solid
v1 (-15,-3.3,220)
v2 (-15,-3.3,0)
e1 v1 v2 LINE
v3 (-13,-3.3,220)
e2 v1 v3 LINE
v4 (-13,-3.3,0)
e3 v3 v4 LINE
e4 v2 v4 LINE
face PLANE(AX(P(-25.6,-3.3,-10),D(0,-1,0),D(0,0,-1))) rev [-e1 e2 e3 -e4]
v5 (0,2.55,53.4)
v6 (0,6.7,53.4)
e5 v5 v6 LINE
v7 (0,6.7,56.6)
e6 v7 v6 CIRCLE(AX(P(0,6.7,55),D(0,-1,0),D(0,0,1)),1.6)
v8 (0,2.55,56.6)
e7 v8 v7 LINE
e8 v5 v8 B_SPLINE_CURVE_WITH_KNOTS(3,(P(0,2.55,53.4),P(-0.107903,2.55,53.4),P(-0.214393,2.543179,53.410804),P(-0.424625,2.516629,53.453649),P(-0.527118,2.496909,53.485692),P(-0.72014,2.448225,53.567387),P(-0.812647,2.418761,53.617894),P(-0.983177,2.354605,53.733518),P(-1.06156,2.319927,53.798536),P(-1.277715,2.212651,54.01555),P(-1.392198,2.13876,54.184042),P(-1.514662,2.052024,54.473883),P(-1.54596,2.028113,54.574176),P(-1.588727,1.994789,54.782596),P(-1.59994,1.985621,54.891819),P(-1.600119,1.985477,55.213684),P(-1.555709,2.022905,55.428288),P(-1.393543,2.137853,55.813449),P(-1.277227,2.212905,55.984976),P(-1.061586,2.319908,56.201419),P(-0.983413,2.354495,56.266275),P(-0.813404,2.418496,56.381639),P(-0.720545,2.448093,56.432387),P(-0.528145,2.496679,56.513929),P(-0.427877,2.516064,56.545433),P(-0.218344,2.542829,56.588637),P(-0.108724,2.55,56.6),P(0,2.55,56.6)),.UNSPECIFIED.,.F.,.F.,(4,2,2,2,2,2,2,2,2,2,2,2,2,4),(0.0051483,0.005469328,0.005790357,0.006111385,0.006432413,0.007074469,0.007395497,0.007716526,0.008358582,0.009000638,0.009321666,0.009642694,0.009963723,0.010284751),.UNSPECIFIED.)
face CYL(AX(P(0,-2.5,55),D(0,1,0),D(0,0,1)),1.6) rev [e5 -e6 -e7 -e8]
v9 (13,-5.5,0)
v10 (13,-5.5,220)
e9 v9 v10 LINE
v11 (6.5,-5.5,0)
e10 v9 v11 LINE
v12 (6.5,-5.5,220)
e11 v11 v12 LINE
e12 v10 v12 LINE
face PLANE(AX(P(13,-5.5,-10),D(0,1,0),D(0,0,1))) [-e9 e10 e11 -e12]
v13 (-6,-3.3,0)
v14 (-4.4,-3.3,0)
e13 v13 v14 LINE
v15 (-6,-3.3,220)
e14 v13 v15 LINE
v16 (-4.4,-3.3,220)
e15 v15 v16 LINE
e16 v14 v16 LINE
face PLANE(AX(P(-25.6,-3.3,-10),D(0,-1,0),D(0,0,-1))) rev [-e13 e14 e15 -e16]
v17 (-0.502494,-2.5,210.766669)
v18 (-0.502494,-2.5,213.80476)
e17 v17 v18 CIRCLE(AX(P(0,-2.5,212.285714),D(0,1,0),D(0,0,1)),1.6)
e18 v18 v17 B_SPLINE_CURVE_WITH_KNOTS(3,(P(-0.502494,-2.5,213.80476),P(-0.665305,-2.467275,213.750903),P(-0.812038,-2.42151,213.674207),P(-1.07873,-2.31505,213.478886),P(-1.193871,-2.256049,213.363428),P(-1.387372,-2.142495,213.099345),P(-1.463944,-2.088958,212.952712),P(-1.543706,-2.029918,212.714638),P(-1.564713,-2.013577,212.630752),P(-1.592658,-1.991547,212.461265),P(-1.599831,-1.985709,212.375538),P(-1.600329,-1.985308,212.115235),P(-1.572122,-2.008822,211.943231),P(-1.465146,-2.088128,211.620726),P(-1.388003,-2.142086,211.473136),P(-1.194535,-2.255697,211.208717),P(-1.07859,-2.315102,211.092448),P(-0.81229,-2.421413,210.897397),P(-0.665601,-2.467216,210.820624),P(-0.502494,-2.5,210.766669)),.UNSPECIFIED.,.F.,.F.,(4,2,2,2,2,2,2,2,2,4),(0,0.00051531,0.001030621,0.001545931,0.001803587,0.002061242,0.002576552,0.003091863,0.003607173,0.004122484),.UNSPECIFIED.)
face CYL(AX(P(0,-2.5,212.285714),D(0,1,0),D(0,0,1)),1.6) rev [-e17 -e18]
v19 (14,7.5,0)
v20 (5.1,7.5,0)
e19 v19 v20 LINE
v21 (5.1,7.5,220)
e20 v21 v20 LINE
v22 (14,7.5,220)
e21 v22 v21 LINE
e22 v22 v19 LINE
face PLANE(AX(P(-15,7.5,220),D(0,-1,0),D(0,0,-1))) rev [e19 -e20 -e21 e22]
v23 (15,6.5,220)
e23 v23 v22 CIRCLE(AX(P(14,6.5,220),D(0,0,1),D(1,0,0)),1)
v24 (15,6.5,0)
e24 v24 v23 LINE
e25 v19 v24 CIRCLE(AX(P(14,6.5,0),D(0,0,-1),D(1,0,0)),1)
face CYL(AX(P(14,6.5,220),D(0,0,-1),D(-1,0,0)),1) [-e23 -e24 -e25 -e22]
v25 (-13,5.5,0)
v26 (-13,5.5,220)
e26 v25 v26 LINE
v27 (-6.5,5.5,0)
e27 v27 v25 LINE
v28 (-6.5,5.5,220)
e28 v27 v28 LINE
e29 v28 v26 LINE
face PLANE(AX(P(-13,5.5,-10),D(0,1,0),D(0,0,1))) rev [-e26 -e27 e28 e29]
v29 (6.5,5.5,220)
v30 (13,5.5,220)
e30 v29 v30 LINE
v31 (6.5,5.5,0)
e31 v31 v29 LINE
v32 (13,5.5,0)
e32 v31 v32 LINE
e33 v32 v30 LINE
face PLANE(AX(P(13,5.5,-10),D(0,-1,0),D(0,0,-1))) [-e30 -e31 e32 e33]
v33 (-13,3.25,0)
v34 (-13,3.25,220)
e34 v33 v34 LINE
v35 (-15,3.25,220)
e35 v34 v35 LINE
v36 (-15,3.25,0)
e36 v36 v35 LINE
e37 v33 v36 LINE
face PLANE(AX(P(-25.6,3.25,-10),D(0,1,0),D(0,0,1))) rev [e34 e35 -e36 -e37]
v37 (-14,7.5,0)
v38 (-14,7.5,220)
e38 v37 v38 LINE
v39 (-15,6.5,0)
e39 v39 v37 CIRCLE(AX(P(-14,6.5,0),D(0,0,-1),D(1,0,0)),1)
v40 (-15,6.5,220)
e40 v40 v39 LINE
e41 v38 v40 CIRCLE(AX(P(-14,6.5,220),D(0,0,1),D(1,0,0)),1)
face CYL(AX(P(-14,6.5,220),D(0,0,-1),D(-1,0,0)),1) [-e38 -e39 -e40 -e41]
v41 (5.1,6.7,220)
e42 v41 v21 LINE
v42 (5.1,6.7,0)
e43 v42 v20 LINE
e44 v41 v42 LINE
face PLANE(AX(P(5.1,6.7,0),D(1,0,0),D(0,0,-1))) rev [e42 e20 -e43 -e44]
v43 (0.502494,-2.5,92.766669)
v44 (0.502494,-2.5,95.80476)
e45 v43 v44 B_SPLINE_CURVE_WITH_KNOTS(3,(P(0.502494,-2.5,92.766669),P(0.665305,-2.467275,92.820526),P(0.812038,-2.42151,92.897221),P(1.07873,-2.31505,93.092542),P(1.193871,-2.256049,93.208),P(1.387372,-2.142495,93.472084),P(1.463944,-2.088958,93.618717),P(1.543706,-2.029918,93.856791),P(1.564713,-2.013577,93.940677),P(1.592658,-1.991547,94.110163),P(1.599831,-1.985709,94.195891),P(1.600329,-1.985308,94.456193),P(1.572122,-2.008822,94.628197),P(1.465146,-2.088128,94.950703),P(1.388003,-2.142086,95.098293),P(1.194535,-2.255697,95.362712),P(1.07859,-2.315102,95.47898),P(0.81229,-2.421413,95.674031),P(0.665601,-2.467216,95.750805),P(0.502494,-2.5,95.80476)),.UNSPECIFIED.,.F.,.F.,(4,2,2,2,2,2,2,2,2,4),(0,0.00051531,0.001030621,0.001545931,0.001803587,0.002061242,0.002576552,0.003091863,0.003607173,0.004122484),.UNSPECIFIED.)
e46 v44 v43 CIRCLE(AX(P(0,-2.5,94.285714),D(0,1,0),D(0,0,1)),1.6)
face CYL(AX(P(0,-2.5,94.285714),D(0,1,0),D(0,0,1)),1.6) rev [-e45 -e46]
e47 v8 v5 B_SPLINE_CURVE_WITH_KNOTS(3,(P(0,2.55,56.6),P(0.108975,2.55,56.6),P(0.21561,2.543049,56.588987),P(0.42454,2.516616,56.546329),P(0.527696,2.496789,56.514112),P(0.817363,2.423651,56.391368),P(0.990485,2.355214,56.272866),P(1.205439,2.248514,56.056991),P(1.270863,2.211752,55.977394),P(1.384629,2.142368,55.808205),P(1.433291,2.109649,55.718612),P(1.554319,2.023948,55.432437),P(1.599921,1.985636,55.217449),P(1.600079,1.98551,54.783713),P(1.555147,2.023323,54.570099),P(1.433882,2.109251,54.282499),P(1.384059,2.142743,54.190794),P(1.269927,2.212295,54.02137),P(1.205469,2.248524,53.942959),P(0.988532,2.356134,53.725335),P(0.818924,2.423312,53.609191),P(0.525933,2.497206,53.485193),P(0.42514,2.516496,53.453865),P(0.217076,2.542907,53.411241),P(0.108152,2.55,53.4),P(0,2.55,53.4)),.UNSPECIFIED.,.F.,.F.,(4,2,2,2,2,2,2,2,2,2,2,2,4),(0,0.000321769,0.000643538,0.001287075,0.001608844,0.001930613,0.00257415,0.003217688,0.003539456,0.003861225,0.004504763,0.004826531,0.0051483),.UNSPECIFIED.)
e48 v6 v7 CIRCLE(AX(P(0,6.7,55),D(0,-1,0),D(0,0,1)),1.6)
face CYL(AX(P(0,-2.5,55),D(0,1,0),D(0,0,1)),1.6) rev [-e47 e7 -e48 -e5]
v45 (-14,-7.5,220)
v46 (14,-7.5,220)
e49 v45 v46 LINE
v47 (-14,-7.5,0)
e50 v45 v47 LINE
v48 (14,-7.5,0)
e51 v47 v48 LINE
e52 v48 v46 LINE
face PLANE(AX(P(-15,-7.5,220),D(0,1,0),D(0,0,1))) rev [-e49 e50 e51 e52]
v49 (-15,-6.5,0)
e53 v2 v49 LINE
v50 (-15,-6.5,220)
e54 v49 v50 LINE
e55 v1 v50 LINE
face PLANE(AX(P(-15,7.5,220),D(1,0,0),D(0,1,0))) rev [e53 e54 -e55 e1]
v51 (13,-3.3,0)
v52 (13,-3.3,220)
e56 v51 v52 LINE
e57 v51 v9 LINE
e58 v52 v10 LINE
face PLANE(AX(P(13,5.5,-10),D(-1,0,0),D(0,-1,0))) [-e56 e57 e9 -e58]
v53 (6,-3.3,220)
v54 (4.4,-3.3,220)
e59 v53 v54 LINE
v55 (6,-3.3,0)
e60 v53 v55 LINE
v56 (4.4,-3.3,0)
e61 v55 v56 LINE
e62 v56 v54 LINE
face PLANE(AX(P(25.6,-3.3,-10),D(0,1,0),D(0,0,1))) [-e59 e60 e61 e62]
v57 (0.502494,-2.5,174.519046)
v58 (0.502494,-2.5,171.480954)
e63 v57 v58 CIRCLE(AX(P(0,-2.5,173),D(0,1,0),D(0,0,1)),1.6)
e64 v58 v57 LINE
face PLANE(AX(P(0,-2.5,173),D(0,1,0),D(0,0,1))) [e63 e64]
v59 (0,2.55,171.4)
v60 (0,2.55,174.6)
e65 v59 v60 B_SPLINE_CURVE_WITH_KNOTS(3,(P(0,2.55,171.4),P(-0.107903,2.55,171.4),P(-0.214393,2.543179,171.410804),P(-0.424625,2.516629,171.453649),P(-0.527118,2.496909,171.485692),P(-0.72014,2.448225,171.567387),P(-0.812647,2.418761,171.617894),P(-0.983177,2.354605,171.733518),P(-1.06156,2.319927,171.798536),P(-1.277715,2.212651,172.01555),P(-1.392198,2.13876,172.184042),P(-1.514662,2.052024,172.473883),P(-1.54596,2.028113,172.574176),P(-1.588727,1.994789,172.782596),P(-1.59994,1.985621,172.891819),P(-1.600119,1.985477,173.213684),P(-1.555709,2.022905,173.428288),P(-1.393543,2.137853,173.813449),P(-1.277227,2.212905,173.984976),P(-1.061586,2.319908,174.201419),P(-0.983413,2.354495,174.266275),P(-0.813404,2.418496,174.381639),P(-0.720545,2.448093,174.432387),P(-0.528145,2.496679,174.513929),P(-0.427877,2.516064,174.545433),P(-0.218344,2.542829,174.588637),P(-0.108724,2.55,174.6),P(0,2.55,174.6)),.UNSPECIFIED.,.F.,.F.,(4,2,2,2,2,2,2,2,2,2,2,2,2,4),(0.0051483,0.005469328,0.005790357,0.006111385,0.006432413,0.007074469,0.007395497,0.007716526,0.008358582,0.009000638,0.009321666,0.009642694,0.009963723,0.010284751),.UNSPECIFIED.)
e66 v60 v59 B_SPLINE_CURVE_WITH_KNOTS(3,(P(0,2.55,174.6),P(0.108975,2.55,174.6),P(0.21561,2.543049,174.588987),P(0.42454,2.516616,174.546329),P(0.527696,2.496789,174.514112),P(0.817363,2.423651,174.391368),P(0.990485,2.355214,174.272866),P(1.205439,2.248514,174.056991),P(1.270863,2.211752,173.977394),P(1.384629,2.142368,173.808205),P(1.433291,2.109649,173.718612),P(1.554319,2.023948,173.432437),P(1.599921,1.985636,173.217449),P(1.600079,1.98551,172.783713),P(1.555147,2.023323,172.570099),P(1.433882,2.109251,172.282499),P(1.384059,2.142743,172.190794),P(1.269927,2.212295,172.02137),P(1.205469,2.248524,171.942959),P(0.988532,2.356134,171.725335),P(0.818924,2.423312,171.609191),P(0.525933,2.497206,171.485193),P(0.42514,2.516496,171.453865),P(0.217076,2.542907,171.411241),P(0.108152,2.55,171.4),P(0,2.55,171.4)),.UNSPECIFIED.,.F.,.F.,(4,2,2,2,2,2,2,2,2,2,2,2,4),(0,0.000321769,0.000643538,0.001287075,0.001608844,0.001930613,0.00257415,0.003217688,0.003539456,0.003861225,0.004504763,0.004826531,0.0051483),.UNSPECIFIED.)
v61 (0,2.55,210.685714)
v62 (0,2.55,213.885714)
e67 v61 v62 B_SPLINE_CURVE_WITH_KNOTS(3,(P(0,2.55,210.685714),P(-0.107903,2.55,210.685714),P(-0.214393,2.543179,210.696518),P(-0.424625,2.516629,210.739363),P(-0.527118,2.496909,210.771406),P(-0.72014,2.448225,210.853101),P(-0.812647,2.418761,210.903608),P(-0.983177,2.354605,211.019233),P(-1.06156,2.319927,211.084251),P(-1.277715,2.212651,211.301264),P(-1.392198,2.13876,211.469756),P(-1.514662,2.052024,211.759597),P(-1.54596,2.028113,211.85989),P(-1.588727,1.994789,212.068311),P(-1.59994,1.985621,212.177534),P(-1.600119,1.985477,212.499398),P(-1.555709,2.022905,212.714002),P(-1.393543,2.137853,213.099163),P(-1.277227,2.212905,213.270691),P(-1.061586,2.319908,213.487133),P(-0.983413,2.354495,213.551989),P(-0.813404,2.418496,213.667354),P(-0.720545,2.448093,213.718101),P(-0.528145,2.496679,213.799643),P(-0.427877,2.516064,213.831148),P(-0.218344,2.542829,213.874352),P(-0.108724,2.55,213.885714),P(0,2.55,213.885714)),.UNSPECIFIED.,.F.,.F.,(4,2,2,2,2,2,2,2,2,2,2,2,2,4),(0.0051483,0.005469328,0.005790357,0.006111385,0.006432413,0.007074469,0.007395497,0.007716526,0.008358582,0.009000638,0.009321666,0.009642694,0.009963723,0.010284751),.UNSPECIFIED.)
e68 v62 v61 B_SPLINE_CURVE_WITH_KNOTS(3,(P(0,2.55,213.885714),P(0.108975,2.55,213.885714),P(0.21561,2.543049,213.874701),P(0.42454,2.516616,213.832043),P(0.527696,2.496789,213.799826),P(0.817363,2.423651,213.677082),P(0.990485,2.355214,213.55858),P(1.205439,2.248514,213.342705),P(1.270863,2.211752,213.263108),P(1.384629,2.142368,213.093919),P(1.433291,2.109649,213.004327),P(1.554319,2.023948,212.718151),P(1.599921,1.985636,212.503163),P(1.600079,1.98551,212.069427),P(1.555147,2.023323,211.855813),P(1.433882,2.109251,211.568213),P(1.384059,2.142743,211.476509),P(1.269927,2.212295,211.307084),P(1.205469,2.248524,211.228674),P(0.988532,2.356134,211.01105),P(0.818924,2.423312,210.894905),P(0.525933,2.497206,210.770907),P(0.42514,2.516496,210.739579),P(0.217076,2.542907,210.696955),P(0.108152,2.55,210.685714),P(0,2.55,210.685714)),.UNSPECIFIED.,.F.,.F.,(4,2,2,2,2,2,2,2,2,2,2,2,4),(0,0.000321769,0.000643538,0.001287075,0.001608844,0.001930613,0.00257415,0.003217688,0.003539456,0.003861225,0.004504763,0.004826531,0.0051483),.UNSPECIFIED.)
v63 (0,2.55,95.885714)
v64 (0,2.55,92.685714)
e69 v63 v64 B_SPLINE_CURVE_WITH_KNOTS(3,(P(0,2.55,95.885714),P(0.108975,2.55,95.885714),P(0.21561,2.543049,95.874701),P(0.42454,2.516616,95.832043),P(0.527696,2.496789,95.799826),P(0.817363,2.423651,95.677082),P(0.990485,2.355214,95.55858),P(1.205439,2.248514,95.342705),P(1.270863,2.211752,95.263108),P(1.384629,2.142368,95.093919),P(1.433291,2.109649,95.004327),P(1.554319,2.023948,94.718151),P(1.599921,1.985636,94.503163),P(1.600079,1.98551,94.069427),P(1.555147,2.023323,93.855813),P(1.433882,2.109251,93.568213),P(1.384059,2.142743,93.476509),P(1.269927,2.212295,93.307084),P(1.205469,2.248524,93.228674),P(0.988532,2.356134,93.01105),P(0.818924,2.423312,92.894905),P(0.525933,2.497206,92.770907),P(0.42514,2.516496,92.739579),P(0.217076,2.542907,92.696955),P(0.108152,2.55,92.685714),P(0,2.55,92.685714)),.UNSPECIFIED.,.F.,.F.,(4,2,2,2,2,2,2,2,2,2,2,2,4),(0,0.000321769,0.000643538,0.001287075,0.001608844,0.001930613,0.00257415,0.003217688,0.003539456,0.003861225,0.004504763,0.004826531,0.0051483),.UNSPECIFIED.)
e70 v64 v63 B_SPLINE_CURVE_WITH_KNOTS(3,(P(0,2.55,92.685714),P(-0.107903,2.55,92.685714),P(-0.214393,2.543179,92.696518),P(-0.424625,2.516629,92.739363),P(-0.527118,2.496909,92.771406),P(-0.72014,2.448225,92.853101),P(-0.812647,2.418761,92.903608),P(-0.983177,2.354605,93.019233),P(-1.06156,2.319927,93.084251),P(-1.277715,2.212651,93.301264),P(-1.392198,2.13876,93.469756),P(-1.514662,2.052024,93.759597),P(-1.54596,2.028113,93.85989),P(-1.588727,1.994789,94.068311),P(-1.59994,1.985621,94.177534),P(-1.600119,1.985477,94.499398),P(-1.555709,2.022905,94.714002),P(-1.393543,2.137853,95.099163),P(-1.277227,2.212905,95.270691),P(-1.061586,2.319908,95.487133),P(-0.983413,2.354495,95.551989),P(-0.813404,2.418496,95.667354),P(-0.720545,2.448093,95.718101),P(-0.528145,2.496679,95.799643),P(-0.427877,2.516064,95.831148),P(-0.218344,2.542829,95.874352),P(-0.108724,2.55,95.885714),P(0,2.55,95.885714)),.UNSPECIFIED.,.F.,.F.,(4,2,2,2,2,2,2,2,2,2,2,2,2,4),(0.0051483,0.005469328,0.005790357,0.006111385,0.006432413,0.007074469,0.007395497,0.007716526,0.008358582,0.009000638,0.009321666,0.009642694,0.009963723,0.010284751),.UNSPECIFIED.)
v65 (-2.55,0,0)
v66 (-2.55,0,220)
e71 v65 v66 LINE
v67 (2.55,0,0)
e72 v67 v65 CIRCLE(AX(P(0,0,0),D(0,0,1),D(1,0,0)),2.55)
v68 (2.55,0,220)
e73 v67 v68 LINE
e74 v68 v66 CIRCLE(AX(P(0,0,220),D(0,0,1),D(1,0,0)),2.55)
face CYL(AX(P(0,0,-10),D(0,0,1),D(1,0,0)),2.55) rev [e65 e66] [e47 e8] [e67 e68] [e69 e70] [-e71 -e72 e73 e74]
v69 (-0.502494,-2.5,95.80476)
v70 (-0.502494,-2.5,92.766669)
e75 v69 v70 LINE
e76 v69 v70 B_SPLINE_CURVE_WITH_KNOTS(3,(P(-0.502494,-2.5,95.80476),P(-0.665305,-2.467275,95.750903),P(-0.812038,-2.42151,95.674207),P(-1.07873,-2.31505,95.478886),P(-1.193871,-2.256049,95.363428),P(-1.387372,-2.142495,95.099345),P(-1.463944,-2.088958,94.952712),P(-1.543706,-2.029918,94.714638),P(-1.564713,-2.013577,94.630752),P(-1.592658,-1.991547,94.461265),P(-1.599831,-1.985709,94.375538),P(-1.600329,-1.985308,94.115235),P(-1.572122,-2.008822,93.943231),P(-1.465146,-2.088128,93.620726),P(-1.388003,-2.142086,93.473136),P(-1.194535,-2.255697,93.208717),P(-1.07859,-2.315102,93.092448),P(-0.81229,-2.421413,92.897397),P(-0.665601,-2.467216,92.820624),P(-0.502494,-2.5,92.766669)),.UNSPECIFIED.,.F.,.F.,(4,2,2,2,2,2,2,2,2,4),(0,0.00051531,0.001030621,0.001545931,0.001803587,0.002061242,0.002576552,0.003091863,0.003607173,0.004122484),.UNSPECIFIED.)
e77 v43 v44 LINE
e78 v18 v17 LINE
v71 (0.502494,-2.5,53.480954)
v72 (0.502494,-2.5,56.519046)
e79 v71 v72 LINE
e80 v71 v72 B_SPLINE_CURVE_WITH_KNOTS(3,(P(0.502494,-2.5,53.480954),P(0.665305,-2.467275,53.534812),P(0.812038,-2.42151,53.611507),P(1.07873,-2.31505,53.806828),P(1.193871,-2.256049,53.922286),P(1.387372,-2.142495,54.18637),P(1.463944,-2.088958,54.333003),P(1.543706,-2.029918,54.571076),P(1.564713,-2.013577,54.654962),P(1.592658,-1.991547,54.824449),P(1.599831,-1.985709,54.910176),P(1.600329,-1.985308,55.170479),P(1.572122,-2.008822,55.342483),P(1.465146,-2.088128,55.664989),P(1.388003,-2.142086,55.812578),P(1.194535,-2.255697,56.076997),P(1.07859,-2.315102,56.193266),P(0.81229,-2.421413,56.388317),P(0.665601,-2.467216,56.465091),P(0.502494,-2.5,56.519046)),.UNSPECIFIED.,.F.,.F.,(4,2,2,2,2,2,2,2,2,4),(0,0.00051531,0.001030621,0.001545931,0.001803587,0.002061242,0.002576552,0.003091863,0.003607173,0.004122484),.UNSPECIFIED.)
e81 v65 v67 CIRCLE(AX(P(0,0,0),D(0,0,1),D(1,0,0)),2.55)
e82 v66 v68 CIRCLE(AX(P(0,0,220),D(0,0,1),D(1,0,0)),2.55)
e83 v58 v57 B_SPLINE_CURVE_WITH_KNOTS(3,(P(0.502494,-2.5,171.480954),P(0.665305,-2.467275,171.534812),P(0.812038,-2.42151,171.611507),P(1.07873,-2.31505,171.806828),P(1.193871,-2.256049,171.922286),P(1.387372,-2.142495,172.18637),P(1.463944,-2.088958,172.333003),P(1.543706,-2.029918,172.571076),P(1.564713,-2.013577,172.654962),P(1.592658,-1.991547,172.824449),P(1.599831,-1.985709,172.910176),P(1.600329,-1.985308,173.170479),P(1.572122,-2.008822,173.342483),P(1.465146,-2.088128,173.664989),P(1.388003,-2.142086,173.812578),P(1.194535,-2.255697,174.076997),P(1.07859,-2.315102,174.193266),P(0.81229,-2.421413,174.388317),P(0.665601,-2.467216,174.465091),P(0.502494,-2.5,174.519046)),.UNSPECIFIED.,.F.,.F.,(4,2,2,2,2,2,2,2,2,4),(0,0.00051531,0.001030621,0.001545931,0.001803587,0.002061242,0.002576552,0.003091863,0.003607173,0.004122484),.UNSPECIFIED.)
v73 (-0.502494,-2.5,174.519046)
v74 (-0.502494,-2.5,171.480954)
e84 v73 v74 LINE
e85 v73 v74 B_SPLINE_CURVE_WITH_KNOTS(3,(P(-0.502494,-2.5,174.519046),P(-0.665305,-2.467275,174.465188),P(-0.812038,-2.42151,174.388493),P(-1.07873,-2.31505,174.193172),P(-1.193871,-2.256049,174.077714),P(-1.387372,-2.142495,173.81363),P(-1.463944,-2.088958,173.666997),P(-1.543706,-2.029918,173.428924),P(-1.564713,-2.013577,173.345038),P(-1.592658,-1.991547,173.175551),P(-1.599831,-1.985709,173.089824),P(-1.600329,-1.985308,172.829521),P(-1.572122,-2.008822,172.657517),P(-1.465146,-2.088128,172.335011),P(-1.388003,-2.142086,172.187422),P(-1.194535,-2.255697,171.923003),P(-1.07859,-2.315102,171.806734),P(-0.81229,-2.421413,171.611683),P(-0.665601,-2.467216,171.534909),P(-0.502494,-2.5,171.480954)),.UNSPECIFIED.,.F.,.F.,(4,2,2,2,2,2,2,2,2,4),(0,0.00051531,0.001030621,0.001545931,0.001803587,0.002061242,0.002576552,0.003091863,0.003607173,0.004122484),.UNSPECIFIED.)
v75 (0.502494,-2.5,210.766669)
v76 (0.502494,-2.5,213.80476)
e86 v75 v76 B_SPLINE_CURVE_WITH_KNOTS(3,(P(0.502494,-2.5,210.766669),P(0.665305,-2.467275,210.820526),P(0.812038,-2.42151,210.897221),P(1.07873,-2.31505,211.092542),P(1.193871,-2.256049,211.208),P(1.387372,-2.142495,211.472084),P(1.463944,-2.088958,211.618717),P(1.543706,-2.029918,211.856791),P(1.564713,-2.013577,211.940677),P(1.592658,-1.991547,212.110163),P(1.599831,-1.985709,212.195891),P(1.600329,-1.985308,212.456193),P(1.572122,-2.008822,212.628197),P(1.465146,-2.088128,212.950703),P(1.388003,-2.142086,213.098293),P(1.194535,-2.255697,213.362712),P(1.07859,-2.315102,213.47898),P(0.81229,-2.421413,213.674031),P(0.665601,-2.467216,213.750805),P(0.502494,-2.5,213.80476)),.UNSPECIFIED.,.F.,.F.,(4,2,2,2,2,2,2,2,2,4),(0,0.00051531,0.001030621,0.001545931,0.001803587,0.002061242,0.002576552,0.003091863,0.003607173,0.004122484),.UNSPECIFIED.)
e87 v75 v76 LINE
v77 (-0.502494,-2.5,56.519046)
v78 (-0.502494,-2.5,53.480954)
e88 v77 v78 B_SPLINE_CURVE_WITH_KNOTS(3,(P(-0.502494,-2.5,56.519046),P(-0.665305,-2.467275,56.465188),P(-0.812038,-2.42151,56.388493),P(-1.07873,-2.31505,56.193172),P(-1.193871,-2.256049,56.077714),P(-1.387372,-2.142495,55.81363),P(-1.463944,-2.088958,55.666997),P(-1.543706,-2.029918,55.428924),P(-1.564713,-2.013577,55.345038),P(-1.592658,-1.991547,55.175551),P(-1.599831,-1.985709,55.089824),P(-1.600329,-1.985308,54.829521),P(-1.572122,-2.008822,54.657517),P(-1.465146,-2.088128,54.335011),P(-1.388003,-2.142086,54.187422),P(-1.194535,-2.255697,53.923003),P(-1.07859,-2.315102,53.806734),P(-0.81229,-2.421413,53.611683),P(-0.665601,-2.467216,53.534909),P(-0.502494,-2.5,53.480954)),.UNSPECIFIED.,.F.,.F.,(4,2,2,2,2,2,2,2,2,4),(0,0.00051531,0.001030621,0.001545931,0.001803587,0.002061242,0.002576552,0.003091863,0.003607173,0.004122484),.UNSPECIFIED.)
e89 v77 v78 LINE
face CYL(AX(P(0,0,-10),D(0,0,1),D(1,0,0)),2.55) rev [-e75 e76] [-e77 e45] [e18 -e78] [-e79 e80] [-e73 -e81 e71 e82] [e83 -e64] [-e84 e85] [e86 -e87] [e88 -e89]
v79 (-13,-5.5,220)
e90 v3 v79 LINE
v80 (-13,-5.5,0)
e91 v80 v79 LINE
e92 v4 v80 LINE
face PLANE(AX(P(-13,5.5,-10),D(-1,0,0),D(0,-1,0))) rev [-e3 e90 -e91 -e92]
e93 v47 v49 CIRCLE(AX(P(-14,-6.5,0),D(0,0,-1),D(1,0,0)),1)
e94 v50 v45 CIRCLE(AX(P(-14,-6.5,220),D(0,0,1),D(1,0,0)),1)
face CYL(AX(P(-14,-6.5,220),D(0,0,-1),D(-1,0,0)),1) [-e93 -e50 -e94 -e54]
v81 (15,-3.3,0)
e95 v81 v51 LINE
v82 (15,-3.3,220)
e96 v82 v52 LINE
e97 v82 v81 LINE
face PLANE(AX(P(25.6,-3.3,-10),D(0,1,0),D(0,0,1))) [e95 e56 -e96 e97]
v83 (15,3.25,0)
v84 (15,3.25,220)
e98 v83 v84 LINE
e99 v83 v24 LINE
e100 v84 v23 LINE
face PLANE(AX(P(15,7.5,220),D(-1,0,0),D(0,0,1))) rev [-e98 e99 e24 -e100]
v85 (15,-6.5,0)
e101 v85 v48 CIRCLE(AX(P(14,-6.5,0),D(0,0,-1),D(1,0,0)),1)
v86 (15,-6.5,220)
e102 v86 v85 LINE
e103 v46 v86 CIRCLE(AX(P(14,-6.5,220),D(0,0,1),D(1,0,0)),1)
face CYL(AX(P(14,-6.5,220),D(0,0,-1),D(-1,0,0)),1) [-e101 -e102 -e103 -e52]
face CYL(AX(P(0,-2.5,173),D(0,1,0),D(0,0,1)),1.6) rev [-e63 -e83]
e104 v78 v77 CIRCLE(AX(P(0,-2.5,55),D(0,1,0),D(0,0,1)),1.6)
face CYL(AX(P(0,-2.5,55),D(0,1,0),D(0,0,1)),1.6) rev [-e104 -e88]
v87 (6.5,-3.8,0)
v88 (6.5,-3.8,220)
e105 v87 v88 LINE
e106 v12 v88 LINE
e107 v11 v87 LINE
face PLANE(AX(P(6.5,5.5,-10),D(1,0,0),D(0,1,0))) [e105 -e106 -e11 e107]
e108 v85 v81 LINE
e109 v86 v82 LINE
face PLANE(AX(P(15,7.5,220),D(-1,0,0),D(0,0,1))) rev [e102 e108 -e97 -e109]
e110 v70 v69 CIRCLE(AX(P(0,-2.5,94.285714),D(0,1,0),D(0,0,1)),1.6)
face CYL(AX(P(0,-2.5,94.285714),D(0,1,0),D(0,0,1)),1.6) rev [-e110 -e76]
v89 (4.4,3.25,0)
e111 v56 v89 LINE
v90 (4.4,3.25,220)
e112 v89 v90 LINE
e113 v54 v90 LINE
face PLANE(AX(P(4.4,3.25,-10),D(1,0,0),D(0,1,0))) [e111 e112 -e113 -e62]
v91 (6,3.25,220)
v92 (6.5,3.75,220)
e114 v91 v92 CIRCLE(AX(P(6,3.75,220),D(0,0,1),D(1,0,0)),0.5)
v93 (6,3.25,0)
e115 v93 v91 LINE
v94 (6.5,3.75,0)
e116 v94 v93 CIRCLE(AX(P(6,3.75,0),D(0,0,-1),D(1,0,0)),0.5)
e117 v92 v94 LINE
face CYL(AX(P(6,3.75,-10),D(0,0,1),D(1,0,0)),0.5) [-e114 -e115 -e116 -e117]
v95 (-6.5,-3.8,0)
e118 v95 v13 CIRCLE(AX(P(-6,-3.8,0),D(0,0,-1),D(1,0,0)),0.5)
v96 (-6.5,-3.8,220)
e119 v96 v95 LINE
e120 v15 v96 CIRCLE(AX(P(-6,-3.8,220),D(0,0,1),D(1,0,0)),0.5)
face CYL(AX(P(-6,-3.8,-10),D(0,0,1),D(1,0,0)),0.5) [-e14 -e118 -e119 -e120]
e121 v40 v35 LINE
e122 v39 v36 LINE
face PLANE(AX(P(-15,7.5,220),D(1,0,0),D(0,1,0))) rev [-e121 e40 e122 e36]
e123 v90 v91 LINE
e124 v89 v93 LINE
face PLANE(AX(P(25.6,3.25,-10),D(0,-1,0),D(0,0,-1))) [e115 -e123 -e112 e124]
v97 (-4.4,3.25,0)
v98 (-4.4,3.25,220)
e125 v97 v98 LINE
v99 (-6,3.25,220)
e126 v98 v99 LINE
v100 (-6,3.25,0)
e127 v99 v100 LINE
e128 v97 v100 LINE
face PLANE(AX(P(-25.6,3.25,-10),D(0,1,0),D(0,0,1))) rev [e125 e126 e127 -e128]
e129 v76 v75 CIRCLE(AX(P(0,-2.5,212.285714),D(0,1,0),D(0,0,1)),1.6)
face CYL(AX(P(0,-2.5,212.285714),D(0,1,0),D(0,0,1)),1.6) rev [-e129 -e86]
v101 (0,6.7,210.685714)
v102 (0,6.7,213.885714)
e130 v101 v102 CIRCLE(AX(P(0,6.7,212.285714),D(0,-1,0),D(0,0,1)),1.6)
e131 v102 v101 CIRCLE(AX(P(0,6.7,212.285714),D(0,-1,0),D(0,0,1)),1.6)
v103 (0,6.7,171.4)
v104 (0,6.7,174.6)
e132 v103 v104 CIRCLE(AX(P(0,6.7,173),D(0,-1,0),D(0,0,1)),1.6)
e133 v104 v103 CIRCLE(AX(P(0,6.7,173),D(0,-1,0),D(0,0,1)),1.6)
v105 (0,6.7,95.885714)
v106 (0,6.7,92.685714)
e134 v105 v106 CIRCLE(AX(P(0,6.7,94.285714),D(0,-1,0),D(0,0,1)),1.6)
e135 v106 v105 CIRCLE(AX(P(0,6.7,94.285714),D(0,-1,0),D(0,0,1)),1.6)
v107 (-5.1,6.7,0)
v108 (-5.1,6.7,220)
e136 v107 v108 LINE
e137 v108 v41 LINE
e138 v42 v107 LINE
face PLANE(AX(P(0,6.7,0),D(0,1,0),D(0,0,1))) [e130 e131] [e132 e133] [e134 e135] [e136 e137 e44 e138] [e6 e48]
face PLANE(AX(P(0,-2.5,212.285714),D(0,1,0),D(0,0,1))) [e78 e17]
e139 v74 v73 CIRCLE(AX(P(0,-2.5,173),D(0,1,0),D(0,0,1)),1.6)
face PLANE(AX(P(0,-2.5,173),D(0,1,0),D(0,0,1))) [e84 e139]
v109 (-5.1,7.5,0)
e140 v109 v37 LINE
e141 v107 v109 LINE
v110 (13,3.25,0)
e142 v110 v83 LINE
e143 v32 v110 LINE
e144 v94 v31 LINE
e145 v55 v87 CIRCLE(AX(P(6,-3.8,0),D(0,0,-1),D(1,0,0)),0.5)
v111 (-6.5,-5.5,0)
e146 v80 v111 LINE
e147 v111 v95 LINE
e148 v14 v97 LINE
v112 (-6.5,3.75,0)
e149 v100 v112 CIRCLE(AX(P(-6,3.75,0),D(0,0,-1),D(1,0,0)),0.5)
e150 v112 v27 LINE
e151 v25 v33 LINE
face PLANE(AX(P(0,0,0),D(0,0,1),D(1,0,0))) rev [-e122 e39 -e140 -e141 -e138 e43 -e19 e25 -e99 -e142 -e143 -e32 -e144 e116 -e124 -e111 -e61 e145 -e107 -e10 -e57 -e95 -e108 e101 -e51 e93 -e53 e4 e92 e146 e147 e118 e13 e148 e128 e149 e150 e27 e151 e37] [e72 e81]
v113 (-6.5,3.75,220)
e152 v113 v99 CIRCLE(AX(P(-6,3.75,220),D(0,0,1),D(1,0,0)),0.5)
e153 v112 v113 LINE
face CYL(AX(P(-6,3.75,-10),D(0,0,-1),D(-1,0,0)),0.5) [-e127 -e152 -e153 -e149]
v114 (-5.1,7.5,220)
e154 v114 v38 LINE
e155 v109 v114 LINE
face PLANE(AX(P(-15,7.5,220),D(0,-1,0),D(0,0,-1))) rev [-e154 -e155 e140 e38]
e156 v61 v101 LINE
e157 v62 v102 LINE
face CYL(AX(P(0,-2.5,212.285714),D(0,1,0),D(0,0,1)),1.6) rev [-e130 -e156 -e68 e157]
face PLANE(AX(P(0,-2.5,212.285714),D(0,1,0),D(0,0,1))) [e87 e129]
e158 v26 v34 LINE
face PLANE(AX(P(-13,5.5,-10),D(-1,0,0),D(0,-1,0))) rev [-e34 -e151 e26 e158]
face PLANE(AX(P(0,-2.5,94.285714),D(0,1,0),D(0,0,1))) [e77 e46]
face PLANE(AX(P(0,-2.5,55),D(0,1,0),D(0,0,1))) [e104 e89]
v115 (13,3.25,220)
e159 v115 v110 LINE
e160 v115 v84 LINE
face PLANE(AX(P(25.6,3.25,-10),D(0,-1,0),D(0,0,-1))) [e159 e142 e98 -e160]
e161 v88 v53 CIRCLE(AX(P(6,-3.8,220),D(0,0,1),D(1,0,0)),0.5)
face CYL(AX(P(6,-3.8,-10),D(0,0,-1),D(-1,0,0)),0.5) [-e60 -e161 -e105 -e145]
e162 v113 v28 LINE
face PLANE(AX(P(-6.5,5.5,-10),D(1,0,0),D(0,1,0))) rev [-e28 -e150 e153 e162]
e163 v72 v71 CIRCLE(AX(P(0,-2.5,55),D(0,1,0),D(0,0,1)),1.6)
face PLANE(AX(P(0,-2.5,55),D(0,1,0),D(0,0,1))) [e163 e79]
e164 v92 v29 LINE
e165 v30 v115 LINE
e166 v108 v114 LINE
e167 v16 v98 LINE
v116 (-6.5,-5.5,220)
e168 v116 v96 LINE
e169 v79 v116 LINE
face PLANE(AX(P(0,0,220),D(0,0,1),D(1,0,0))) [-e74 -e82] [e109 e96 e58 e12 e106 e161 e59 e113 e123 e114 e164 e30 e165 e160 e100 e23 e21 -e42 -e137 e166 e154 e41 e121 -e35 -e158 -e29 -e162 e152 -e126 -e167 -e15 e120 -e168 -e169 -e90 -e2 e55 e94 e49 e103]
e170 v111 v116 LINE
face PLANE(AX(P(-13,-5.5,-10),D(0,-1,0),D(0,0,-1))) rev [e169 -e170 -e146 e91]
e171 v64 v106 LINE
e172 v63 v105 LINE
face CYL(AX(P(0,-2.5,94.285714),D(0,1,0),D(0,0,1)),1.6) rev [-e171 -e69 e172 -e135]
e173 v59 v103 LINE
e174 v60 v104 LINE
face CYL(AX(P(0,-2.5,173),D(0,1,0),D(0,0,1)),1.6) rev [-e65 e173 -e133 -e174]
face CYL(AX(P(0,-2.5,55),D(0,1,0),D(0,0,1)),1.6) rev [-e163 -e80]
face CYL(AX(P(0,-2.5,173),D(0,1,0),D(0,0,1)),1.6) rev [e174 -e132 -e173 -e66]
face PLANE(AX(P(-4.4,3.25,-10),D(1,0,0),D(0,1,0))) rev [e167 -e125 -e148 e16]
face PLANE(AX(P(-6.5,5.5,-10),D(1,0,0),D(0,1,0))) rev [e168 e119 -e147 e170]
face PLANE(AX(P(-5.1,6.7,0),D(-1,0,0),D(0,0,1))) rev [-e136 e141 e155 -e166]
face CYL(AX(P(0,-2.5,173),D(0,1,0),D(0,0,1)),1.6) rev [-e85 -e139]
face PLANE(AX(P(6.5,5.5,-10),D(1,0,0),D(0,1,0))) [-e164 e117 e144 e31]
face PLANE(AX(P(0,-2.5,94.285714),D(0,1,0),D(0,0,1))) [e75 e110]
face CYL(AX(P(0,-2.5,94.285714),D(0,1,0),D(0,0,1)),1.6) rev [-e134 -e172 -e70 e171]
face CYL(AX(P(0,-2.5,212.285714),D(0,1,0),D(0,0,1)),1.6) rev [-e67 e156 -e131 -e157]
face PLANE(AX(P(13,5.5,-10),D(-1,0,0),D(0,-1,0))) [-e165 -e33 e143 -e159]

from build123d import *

# Parameters (mm, degrees)
SKETCH_1_W             = 30
SKETCH_1_H             = 15
EXTRUDE_1_DEPTH        = 220
FILLET_1_R             = 1
SKETCH_2_R             = 2.55
CUT_EXTRUDE_1_DEPTH    = 230
SKETCH_3_W             = 21.2
SKETCH_3_H             = 6.55
CUT_EXTRUDE_2_DEPTH    = 230
SKETCH_4_W             = 6.5
SKETCH_4_H             = 11
CUT_EXTRUDE_3_DEPTH    = 230
FILLET_2_R             = 0.5
SKETCH_5_R             = 1.6
CUT_EXTRUDE_4_DEPTH    = 10
PATTERN_LINEAR_1_COUNT = 2
PATTERN_LINEAR_1_PITCH = 118
SKETCH_7_W             = 10.2
SKETCH_7_H             = 220
CUT_EXTRUDE_6_DEPTH    = 0.8


with BuildPart() as part:
    # 草图1 → 凸台-拉伸1 (new body)
    with BuildSketch(Plane.XY):
        Rectangle(SKETCH_1_W, SKETCH_1_H)
    extrude(amount=EXTRUDE_1_DEPTH)

    # 圆角1
    fillet_1_edges = [part.edges().sort_by_distance(p)[0] for p in [
        (15, -7.5, 110),
        (-15, -7.5, 110),
        (-15, 7.5, 110),
        (15, 7.5, 110),
    ]]
    fillet(fillet_1_edges, radius=FILLET_1_R)

    # 草图2 → 切除-拉伸1 (cut)
    with BuildSketch(Plane.XY.offset(220)):
        Circle(SKETCH_2_R)
    extrude(amount=-CUT_EXTRUDE_1_DEPTH, mode=Mode.SUBTRACT)

    # 草图3 → 切除-拉伸2 (cut)
    with BuildSketch(Plane.XY.offset(220)):
        with Locations((-15, -0.025)):
            Rectangle(SKETCH_3_W, SKETCH_3_H)
    cut_extrude_2 = extrude(amount=-CUT_EXTRUDE_2_DEPTH, mode=Mode.SUBTRACT)

    # 镜向1: 切除-拉伸2 across plane
    add(cut_extrude_2.mirror(Plane(origin=(0, 0, 0), x_dir=(0, 0, 1), z_dir=(1, 0, 0))), mode=Mode.SUBTRACT)

    # 草图4 → 切除-拉伸3 (cut)
    with BuildSketch(Plane.XY.offset(220)):
        with Locations((-9.75, 0)):
            Rectangle(SKETCH_4_W, SKETCH_4_H)
    cut_extrude_3 = extrude(amount=-CUT_EXTRUDE_3_DEPTH, mode=Mode.SUBTRACT)

    # 镜向2: 切除-拉伸3 across plane
    add(cut_extrude_3.mirror(Plane(origin=(0, 0, 0), x_dir=(0, 0, 1), z_dir=(1, 0, 0))), mode=Mode.SUBTRACT)

    # 圆角2
    fillet_2_edges = [part.edges().sort_by_distance(p)[0] for p in [
        (6.5, -3.3, 110),
        (6.5, 3.25, 110),
        (-6.5, 3.25, 110),
        (-6.5, -3.3, 110),
    ]]
    fillet(fillet_2_edges, radius=FILLET_2_R)

    # 草图5 → 切除-拉伸4 (cut)
    with BuildSketch(Plane(origin=(0, 7.5, 0), x_dir=(1, 0, 0), z_dir=(0, 1, 0))):
        with Locations(Location((0, -55, 0), (0, 0, 270))):
            Circle(SKETCH_5_R)
        with Locations(Location((0, -94.285714286, 0), (0, 0, 270))):
            Circle(SKETCH_5_R)
    cut_extrude_4 = extrude(amount=-CUT_EXTRUDE_4_DEPTH, mode=Mode.SUBTRACT)

    # 阵列(线性)1: 切除-拉伸4 ×2
    with Locations(*[(0, 0, i * PATTERN_LINEAR_1_PITCH) for i in range(1, PATTERN_LINEAR_1_COUNT)]):
        add(cut_extrude_4, mode=Mode.SUBTRACT)

    # 草图7 → 切除-拉伸6 (cut)
    with BuildSketch(Plane(origin=(0, 7.5, 0), x_dir=(1, 0, 0), z_dir=(0, 1, 0))):
        with Locations((0, -110)):
            Rectangle(SKETCH_7_W, SKETCH_7_H)
    extrude(amount=-CUT_EXTRUDE_6_DEPTH, mode=Mode.SUBTRACT)


solid = part.part
